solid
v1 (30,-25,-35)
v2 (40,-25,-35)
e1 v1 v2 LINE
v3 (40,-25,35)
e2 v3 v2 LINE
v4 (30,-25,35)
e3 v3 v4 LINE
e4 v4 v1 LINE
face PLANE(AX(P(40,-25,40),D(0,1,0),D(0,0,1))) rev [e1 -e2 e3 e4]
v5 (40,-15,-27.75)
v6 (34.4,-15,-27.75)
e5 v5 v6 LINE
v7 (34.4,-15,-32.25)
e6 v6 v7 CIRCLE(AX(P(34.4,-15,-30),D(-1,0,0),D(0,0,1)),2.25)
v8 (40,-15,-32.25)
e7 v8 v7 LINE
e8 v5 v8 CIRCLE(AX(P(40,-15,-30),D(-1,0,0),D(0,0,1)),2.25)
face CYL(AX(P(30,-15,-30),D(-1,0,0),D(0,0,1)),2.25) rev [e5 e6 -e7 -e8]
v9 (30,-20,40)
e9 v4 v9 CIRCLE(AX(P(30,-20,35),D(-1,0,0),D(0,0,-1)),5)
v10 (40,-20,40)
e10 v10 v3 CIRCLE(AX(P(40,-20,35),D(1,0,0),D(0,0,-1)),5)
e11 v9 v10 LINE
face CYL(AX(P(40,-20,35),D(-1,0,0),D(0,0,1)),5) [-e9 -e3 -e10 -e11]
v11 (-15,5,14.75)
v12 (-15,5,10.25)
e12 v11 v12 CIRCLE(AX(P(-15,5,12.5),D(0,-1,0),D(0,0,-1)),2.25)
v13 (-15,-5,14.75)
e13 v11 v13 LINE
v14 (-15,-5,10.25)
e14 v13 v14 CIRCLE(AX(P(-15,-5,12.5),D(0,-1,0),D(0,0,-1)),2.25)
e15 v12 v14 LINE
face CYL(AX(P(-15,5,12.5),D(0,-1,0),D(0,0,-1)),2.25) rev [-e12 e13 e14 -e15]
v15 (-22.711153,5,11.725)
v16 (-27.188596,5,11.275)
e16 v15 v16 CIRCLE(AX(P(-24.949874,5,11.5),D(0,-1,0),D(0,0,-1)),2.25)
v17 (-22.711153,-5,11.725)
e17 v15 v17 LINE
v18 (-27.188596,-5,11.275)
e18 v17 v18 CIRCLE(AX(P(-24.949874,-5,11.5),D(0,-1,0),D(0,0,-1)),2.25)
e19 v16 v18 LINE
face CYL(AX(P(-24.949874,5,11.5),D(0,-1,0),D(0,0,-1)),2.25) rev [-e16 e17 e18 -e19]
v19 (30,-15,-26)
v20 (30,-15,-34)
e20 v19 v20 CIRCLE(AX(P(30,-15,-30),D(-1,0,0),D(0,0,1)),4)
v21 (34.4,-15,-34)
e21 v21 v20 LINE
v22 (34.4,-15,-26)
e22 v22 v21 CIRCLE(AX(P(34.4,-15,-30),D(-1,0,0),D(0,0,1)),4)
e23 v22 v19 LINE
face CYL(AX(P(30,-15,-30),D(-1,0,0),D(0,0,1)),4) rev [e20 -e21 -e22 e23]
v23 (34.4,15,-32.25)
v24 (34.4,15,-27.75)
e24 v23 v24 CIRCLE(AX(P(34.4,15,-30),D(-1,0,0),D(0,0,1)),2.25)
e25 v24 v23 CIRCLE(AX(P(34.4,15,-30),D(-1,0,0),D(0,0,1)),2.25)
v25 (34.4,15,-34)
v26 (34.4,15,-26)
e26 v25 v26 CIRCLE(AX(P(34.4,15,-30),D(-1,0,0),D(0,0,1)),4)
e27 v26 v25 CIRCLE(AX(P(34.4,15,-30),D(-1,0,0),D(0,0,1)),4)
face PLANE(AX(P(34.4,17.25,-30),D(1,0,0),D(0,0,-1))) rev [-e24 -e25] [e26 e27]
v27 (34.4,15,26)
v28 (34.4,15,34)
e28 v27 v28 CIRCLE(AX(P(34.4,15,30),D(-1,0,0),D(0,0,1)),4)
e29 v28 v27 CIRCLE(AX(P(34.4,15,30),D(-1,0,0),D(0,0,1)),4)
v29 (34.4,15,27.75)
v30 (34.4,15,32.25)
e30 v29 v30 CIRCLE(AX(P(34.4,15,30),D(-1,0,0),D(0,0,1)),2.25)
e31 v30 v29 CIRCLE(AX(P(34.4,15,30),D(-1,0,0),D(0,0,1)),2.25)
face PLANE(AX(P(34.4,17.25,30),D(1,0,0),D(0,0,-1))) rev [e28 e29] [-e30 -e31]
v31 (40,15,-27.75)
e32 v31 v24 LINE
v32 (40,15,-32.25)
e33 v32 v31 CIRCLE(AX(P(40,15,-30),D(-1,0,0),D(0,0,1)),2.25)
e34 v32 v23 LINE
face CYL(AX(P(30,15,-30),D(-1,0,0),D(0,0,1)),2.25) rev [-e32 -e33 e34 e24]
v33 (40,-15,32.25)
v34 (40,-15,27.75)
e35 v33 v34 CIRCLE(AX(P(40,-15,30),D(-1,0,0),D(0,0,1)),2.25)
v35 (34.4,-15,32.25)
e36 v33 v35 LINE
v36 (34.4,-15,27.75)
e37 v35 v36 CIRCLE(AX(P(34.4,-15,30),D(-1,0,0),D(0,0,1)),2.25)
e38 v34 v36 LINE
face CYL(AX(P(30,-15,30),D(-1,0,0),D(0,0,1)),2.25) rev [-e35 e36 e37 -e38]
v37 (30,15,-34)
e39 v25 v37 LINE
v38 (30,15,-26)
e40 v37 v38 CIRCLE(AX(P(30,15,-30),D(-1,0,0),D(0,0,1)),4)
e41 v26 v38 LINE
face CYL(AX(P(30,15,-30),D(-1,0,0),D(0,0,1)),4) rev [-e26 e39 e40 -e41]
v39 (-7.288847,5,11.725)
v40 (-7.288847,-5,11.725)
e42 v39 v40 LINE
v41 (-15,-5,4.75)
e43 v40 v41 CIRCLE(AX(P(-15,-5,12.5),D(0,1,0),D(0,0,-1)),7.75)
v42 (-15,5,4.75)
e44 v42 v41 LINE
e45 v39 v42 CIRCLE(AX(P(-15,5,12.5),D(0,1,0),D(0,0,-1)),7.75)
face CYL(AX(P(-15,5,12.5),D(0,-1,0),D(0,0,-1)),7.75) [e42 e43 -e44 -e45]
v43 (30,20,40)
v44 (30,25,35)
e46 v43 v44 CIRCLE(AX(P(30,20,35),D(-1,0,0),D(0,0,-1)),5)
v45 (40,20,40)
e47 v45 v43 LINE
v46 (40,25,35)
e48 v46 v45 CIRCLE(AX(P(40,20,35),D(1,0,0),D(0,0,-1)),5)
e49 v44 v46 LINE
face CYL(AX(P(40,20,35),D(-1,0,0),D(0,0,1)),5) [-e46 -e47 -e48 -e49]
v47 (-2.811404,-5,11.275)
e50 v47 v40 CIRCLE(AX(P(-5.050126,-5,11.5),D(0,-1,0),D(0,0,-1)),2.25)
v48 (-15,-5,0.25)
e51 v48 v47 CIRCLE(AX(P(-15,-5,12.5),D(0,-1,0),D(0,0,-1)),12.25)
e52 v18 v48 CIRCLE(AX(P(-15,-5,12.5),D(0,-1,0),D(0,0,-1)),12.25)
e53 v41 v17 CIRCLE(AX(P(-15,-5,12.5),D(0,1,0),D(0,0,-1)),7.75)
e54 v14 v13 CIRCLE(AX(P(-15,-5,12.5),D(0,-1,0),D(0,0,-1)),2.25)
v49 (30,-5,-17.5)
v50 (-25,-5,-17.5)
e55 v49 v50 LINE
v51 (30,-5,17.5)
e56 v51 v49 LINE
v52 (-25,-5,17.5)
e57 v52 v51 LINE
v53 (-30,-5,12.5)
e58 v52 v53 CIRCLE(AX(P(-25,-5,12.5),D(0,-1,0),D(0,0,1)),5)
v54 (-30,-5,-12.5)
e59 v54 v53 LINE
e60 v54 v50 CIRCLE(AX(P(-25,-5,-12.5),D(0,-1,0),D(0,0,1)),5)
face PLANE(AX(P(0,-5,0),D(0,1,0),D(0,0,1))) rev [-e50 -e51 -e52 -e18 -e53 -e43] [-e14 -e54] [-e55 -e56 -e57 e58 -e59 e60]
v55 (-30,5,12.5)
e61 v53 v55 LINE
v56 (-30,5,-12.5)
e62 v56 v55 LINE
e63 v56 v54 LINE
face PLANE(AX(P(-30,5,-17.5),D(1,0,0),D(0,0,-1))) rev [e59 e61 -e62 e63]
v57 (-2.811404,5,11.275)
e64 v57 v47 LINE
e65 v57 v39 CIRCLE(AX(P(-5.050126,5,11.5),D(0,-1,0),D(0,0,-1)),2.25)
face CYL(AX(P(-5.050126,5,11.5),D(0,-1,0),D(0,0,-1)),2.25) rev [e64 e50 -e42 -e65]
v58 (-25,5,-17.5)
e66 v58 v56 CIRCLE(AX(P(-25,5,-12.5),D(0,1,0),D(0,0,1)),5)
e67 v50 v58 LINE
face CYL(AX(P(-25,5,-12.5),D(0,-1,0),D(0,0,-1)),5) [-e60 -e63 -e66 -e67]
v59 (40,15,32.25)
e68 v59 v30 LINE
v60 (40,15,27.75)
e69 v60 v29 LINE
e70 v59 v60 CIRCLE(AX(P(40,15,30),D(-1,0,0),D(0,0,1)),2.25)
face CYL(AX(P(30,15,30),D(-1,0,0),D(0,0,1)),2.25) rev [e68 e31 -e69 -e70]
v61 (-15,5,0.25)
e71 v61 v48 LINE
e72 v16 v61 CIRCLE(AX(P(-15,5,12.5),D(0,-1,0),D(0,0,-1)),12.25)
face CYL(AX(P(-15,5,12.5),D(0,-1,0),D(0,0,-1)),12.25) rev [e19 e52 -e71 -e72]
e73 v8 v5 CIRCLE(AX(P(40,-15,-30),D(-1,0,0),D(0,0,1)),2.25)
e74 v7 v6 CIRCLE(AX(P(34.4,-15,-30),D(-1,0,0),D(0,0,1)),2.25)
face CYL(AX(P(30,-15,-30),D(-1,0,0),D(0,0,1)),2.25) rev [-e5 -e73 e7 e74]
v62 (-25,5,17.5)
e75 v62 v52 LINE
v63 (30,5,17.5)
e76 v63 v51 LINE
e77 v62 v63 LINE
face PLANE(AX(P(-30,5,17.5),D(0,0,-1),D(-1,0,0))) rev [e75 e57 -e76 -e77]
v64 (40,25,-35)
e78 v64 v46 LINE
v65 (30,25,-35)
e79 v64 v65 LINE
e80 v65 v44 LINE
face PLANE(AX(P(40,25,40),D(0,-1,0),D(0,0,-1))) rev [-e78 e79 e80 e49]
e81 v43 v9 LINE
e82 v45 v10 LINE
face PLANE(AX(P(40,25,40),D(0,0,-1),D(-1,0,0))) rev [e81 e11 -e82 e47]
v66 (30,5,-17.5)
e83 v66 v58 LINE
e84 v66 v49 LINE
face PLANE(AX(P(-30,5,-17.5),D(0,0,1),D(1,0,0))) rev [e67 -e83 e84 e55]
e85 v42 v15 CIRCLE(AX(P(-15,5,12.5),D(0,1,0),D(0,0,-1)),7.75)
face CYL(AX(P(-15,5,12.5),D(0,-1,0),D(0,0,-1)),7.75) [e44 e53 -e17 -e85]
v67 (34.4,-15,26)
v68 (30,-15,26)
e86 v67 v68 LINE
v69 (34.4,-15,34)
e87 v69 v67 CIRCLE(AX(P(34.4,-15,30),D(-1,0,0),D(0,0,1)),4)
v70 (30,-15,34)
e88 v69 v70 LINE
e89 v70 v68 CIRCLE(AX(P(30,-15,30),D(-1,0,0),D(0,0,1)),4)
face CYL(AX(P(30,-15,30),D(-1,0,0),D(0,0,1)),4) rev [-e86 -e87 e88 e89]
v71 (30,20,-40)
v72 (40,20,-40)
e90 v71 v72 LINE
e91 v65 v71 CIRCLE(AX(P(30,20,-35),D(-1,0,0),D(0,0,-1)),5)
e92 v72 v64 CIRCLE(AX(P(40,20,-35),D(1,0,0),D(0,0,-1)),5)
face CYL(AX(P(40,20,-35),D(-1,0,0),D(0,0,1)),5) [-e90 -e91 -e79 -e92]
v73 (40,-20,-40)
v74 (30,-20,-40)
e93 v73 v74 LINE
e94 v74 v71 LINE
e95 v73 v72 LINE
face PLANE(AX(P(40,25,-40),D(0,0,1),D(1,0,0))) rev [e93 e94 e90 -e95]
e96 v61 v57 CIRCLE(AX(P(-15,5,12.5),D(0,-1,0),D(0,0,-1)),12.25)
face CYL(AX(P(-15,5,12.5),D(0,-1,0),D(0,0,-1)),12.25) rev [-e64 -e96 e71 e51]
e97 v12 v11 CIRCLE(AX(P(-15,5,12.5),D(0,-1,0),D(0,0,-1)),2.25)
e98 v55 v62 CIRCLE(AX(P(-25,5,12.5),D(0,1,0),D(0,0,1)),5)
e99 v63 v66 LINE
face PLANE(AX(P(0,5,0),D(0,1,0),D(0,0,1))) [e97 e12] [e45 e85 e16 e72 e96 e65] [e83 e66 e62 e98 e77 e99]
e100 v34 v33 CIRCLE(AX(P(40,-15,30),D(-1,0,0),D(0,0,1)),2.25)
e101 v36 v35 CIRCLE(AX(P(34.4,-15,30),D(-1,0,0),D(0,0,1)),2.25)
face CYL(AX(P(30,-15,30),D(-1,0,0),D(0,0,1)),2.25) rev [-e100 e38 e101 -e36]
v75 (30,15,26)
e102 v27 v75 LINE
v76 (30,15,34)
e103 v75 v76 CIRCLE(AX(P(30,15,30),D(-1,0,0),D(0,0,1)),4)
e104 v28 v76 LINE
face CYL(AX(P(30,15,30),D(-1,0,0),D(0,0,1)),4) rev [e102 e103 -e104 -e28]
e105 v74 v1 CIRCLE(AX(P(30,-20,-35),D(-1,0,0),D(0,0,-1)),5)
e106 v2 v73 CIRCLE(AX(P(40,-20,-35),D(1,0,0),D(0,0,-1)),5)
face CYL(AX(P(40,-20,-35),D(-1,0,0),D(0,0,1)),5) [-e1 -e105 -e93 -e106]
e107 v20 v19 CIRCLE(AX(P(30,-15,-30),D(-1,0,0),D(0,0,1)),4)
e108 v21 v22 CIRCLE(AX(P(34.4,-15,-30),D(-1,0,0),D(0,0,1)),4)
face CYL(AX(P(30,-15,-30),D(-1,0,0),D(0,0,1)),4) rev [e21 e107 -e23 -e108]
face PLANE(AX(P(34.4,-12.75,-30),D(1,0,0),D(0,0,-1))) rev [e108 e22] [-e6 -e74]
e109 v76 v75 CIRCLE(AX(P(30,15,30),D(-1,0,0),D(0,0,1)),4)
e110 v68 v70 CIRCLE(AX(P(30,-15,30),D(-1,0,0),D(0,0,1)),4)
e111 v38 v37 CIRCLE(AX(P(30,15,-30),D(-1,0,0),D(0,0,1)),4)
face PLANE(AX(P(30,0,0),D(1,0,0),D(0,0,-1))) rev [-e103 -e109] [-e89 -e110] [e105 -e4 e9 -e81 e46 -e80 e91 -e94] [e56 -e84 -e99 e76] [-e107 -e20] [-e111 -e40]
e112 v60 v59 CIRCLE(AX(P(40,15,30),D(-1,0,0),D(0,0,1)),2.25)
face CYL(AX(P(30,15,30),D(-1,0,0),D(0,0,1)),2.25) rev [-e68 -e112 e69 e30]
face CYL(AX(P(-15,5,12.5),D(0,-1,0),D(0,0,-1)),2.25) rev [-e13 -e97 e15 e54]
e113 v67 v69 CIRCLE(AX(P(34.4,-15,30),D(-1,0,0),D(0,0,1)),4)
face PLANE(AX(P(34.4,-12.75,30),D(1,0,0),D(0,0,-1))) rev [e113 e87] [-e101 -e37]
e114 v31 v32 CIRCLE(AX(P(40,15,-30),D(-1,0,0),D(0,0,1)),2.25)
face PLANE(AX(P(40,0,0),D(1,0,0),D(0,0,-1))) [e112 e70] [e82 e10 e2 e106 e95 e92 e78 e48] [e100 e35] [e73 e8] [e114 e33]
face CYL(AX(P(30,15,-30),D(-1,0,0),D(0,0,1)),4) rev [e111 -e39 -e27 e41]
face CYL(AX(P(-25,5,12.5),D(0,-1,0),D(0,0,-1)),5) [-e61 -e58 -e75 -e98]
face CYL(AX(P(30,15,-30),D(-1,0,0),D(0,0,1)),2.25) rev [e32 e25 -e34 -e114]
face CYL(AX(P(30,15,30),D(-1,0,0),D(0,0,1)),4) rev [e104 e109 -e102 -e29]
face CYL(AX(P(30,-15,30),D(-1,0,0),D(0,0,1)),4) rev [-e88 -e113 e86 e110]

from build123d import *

# Parameters (mm, degrees)
SKETCH_1_W                   = 60
SKETCH_1_H                   = 35
EXTRUDE_1_DEPTH              = 5
SKETCH_2_R                   = 2.25
CUT_EXTRUDE_1_DEPTH          = 37.142080737
CUT_EXTRUDE_2_DEPTH          = 37.142080737
SKETCH_5_W                   = 80
SKETCH_5_H                   = 50
EXTRUDE_3_DEPTH              = 10
HOLE_WIZARD_M4_1_D           = 4.5
HOLE_WIZARD_M4_1_CBORE_D     = 8
HOLE_WIZARD_M4_1_CBORE_DEPTH = 4.4
FILLET_1_R                   = 5


with BuildPart() as part:
    # 草图1 → 凸台-拉伸1 (new, symmetric)
    with BuildSketch(Plane(origin=(0, 0, 0), x_dir=(1, 0, 0), z_dir=(0, 1, 0))):
        Rectangle(SKETCH_1_W, SKETCH_1_H)
    extrude(amount=EXTRUDE_1_DEPTH, both=True)

    # 草图2 → 切除-拉伸1 (cut, through all)
    with BuildSketch(Plane.XZ.offset(5)):
        with Locations(Location((-15, 12.5, 0), (0, 0, 270))):
            Circle(SKETCH_2_R)
        with Locations(Location((-15, 2.5, 0), (0, 0, 270))):
            Circle(SKETCH_2_R)
    extrude(amount=-CUT_EXTRUDE_1_DEPTH, mode=Mode.SUBTRACT)

    # 草图3 → 切除-拉伸2 (cut, through all)
    with BuildSketch(Plane.XZ.offset(5)):
        with BuildLine():
            ThreePointArc((-27.188596105, 11.275), (-15, 0.25), (-2.811403895, 11.275))
            ThreePointArc((-2.811403895, 11.275), (-4.825125629, 13.738721733), (-7.288847362, 11.725))
            ThreePointArc((-7.288847362, 11.725), (-15, 4.75), (-22.711152638, 11.725))
            ThreePointArc((-22.711152638, 11.725), (-25.174874371, 13.738721733), (-27.188596105, 11.275))
        make_face()
    extrude(amount=-CUT_EXTRUDE_2_DEPTH, mode=Mode.SUBTRACT)

    # 草图5 → 凸台-拉伸3 (add)
    with BuildSketch(Plane(origin=(30, 0, 0), x_dir=(0, 0, -1), z_dir=(1, 0, 0))):
        Rectangle(SKETCH_5_W, SKETCH_5_H)
    extrude(amount=EXTRUDE_3_DEPTH)

    # M4 六角凹头螺钉的柱形沉头孔1 (through all)
    with Locations(Plane.ZY.offset(-30)):
        with Locations((30, 15), (-30, 15), (-30, -15), (30, -15)):
            CounterBoreHole(HOLE_WIZARD_M4_1_D / 2, HOLE_WIZARD_M4_1_CBORE_D / 2, HOLE_WIZARD_M4_1_CBORE_DEPTH)

    # 圆角1
    fillet_1_edges = [part.edges().sort_by_distance(p)[0] for p in [
        (35, -25, -40),
        (35, 25, -40),
        (35, 25, 40),
        (35, -25, 40),
        (-30, 0, 17.5),
        (-30, 0, -17.5),
    ]]
    fillet(fillet_1_edges, radius=FILLET_1_R)


solid = part.part
